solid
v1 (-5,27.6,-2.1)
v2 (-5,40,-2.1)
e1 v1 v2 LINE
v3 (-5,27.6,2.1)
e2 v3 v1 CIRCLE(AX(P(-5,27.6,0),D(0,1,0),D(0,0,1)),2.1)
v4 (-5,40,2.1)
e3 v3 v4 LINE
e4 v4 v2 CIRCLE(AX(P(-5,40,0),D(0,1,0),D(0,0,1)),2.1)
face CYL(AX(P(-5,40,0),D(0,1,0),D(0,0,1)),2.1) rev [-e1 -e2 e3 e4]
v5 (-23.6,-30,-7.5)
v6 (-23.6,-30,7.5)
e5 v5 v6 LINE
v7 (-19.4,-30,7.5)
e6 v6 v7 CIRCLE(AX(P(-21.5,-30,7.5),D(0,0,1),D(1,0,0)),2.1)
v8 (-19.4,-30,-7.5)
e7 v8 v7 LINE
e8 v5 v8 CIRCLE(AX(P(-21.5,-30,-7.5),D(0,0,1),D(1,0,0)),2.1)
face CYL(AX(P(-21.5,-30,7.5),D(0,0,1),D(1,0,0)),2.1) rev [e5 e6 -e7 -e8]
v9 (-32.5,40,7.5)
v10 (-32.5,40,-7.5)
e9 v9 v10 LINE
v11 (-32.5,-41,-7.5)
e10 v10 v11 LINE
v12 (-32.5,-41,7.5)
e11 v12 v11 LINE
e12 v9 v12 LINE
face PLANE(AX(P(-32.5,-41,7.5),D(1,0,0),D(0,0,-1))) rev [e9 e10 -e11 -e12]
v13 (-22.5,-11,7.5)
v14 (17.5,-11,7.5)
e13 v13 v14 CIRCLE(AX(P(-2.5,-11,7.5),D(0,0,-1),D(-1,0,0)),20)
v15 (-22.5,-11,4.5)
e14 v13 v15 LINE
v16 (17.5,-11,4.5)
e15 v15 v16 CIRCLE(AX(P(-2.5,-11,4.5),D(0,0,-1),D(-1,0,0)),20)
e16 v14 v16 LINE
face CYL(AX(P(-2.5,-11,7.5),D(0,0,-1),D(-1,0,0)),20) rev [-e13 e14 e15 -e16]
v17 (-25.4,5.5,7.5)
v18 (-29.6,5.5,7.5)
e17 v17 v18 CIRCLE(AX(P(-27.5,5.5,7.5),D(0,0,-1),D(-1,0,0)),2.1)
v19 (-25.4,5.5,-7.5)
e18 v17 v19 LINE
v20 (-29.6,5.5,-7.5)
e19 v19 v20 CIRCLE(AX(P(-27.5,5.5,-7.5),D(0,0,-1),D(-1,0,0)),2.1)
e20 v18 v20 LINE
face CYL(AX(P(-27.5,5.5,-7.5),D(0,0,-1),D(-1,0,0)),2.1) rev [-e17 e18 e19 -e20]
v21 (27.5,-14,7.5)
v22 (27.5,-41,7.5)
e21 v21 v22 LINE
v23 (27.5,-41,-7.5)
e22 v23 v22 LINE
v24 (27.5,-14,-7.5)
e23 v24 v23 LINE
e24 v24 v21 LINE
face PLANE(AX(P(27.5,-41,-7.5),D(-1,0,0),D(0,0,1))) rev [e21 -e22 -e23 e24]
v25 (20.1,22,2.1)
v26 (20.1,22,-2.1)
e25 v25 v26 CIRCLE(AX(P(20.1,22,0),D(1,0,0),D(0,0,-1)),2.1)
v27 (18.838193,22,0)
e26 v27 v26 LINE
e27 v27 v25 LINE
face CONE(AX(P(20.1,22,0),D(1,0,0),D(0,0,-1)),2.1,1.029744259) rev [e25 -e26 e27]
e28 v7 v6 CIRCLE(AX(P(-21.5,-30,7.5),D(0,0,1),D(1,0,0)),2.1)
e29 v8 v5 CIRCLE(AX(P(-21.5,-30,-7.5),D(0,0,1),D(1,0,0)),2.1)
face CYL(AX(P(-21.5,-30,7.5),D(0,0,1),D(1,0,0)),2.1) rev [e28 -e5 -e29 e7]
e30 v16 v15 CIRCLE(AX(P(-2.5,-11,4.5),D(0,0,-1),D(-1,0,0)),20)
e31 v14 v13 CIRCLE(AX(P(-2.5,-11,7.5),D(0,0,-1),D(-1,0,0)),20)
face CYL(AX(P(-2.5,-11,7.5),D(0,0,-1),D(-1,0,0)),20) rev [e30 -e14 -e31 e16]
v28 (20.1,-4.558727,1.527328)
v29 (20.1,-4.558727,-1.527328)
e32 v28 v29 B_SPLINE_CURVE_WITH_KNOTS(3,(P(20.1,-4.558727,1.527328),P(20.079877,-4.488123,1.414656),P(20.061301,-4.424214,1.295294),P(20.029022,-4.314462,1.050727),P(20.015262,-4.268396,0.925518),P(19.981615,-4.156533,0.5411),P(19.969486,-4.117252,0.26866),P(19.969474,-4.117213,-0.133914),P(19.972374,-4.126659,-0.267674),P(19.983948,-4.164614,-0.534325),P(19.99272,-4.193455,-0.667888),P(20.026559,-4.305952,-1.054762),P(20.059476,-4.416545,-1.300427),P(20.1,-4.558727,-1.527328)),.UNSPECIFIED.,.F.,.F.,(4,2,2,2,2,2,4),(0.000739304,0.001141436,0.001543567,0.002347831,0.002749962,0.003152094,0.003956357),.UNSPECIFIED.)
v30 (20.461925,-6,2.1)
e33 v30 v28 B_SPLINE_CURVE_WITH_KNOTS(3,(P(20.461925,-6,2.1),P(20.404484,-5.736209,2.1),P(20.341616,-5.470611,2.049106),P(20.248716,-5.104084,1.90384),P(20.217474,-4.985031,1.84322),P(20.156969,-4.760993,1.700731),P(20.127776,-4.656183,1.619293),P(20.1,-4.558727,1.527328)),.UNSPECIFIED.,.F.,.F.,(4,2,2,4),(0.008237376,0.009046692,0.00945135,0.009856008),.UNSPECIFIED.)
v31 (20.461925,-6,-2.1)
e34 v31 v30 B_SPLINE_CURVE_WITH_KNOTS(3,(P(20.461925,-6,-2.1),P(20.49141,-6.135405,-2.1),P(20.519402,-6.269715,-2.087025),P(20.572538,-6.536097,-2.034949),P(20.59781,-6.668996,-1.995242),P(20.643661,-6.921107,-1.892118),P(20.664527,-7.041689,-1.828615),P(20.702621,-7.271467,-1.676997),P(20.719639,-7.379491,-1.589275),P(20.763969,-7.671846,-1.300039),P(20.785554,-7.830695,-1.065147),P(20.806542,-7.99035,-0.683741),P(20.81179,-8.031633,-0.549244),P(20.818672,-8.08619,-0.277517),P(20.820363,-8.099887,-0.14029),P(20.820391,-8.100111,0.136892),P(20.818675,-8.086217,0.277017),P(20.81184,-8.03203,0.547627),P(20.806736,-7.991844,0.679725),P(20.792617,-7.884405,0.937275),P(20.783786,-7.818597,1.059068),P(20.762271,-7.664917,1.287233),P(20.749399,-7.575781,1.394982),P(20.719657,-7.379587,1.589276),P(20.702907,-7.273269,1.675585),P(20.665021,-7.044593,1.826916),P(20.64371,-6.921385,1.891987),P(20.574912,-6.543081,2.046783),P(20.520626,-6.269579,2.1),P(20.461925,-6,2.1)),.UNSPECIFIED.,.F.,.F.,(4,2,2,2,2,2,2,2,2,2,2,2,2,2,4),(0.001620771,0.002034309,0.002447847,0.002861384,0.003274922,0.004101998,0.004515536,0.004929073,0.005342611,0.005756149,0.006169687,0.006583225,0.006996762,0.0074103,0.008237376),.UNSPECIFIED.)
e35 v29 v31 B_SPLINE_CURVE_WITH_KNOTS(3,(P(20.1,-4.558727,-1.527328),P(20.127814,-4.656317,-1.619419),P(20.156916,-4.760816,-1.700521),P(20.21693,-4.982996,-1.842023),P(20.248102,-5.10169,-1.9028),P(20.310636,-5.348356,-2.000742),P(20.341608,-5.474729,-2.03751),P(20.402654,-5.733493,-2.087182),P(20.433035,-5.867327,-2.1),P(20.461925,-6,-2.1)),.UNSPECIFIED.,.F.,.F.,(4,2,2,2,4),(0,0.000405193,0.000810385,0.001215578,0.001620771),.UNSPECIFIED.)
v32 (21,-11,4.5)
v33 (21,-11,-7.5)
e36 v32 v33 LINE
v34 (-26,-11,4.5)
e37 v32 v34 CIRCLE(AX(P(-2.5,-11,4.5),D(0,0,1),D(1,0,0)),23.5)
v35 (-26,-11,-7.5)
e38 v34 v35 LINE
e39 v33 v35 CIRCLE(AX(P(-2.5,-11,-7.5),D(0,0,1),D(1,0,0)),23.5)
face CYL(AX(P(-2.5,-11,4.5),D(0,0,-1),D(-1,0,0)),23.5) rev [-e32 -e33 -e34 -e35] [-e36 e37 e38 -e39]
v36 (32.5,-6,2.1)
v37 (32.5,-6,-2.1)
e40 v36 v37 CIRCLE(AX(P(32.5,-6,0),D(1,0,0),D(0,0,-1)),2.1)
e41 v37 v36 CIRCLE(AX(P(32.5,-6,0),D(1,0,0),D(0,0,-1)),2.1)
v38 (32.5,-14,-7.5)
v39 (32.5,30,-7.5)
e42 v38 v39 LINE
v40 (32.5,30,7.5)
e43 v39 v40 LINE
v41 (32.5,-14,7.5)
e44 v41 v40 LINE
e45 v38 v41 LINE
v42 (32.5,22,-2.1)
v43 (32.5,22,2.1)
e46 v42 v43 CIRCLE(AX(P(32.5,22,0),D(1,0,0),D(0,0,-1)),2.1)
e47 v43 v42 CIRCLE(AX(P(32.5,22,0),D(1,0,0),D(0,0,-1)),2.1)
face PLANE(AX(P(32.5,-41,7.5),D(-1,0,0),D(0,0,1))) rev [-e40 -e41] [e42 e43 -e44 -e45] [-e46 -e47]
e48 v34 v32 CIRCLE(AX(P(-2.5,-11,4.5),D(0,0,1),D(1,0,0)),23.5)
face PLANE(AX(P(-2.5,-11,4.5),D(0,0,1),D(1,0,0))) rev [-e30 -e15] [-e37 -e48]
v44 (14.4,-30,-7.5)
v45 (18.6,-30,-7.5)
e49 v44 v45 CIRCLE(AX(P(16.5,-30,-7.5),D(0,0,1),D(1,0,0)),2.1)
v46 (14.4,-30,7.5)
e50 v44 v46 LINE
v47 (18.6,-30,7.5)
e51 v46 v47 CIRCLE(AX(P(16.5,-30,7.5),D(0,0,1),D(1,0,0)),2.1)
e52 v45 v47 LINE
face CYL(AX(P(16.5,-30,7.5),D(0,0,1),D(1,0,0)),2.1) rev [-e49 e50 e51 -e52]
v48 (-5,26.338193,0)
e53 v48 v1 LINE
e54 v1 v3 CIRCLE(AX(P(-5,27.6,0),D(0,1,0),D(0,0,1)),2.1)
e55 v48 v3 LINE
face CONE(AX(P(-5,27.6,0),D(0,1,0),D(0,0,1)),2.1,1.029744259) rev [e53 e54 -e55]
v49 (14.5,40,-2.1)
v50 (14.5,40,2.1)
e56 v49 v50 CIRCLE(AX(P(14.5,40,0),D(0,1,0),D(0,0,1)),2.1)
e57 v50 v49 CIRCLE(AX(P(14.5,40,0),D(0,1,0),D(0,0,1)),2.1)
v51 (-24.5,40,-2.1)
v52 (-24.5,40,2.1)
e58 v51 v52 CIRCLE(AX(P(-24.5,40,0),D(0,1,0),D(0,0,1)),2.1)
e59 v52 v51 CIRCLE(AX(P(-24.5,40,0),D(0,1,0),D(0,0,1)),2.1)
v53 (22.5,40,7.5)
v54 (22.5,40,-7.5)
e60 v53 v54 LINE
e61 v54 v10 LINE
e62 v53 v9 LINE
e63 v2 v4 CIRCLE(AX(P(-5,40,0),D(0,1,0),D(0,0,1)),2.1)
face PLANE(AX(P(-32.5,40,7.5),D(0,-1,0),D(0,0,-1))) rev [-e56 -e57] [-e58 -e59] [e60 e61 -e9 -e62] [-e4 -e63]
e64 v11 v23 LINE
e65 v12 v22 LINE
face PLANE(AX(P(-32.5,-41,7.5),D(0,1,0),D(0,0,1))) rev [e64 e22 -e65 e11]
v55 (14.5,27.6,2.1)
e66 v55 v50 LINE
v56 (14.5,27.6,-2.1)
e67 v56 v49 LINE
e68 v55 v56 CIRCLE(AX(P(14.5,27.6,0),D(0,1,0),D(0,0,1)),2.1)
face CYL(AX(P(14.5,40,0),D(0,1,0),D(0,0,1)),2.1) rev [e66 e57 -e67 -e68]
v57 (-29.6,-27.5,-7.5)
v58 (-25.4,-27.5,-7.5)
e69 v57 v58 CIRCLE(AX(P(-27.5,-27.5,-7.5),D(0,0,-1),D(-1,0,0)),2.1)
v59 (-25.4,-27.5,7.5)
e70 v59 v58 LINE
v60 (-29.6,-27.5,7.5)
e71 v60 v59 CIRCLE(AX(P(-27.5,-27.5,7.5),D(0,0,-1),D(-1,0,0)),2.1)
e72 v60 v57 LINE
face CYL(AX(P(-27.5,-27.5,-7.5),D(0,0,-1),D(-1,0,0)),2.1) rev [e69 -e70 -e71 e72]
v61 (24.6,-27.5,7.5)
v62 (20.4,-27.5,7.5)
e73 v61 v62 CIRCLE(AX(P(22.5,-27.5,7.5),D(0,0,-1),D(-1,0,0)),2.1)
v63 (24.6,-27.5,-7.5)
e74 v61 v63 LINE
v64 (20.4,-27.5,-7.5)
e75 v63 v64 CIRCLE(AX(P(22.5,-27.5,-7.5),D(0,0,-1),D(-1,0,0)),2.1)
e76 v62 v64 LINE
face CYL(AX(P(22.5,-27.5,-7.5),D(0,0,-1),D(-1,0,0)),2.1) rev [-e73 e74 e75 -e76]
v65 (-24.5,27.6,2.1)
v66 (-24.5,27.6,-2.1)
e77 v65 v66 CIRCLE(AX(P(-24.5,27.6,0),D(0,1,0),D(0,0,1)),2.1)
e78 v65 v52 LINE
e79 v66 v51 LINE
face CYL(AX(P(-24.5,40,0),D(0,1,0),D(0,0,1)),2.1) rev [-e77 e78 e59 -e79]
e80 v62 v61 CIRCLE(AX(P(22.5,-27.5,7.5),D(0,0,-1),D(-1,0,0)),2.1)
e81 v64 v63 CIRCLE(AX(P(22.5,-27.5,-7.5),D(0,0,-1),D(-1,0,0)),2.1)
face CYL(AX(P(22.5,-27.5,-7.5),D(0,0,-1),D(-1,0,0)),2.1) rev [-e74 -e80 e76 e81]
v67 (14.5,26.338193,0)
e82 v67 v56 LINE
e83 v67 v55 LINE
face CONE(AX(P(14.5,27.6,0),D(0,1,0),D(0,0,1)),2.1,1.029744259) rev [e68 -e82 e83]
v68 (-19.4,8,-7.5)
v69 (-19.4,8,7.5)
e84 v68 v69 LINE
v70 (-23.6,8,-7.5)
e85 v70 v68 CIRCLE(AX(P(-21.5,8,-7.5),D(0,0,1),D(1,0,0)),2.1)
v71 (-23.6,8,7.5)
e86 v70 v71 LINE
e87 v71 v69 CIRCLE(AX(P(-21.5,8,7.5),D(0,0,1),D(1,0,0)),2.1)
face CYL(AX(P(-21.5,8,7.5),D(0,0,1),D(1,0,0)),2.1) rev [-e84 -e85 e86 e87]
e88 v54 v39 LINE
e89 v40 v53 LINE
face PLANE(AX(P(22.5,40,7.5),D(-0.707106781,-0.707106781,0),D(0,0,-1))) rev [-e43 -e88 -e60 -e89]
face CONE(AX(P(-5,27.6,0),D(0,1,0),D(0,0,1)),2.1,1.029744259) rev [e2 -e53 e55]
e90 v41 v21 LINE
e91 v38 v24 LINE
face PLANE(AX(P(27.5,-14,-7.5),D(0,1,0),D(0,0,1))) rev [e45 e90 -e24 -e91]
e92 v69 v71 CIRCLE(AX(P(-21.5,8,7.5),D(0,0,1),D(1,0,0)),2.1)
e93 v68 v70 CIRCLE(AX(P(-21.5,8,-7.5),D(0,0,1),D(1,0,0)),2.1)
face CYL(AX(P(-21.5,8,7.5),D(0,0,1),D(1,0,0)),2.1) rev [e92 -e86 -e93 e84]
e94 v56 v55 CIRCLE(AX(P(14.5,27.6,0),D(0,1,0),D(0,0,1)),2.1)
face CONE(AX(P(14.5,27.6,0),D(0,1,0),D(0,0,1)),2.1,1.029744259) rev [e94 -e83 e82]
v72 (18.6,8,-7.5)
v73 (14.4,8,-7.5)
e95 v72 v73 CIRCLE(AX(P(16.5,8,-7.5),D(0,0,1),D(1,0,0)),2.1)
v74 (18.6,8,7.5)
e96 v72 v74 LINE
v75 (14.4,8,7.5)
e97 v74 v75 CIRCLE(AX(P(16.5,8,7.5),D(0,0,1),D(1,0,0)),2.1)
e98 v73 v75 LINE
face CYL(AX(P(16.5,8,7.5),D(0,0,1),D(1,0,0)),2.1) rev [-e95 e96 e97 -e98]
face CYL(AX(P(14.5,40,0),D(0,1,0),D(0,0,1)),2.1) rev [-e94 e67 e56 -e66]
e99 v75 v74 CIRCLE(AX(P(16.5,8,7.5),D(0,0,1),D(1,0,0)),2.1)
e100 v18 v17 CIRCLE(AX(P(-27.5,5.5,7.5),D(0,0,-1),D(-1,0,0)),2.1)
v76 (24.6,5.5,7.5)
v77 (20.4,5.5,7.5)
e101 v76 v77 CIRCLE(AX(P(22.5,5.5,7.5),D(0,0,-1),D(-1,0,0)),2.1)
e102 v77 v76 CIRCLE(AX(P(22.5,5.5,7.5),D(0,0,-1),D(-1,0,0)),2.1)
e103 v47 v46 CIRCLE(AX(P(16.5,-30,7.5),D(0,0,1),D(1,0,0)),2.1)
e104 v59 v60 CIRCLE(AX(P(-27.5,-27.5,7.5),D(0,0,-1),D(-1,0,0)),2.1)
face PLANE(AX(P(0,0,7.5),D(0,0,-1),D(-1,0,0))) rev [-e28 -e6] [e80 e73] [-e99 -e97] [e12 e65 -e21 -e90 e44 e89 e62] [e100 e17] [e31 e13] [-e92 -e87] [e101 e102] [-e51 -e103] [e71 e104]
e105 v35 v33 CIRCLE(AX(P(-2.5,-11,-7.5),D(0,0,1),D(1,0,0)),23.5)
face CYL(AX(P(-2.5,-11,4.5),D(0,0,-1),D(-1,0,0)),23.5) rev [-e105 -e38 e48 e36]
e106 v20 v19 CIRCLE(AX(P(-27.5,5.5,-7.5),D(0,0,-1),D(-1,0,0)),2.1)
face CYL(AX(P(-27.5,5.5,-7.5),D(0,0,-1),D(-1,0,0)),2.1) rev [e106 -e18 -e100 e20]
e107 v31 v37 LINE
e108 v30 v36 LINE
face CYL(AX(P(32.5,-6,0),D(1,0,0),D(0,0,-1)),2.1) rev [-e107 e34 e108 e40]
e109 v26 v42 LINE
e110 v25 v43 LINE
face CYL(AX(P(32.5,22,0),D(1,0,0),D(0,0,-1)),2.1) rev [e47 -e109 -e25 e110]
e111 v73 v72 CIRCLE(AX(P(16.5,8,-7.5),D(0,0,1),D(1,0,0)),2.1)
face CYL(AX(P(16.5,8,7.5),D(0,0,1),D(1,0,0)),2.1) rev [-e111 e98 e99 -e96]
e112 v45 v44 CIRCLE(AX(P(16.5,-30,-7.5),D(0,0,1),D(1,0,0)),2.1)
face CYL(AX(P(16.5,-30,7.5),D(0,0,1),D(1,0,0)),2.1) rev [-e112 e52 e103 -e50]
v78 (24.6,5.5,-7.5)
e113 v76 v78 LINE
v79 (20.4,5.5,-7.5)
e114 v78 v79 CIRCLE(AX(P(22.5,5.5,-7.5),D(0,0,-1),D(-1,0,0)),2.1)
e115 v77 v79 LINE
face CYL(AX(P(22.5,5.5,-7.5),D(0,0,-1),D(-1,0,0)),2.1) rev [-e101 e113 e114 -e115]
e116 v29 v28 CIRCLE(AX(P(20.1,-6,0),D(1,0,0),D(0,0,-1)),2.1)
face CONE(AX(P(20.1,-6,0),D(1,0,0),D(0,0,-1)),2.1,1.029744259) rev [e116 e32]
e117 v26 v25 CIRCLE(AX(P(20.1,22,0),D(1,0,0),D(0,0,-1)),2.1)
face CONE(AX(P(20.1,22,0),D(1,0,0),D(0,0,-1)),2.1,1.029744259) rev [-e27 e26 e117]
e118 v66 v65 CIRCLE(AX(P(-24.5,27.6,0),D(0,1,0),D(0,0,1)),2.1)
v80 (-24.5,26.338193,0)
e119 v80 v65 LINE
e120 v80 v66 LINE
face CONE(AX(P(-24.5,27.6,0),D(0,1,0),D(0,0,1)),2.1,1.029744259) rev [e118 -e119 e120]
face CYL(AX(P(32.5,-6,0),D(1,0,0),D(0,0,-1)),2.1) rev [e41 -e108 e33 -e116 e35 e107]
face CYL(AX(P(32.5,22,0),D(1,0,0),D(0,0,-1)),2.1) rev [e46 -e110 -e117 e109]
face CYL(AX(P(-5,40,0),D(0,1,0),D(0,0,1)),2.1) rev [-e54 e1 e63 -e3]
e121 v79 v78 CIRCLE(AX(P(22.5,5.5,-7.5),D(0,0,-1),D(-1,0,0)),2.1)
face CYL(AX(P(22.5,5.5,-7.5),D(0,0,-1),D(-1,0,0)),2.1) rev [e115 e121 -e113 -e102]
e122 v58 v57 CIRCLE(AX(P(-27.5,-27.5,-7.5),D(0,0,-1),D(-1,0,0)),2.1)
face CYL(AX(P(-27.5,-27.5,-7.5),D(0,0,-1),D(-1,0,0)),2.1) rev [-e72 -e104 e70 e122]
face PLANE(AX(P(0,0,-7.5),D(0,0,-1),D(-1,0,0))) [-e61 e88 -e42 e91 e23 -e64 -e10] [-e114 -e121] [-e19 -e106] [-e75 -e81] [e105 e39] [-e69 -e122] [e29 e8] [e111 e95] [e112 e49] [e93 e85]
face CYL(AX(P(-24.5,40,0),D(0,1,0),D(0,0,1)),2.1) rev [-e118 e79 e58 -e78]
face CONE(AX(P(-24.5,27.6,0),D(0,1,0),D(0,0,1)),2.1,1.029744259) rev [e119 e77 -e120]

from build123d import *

# Parameters (mm, degrees)
SKETCH_1_W             = 65
SKETCH_1_H             = 82
EXTRUDE_1_DEPTH        = 7.5
SKETCH_10_R            = 23.5
CUT_EXTRUDE_1_DEPTH    = 12
SKETCH_12_R            = 20
CUT_EXTRUDE_2_DEPTH    = 54.677276384
SKETCH_13_W            = 5
SKETCH_13_H            = 27
CUT_EXTRUDE_3_DEPTH    = 55.426556018
HOLE_WIZARD_M5_1_D     = 4.2
HOLE_WIZARD_M5_2_D     = 4.2
MOVE_FACE_1_BY         = 1
HOLE_WIZARD_M5_4_D     = 4.2
HOLE_WIZARD_M5_4_DEPTH = 12.4
HOLE_WIZARD_M5_4_TIP   = 1.2618073
CHAMFER_2_SIZE         = 10
HOLE_WIZARD_M5_3_D     = 4.2
HOLE_WIZARD_M5_3_DEPTH = 12.4
HOLE_WIZARD_M5_3_TIP   = 1.2618073


with BuildPart() as part:
    # 草图1 → 凸台-拉伸1 (new, symmetric)
    with BuildSketch(Plane.XY):
        Rectangle(SKETCH_1_W, SKETCH_1_H)
    extrude(amount=EXTRUDE_1_DEPTH, both=True)

    # 草图10 → 切除-拉伸1 (cut)
    with BuildSketch(Plane.XY.offset(-7.5)):
        with Locations((-2.5, -11)):
            Circle(SKETCH_10_R)
    extrude(amount=CUT_EXTRUDE_1_DEPTH, mode=Mode.SUBTRACT)

    # 草图12 → 切除-拉伸2 (cut, through all)
    with BuildSketch(Plane(origin=(0, 0, 4.5), x_dir=(-1, 0, 0), z_dir=(0, 0, -1))):
        with Locations((2.5, -11)):
            Circle(SKETCH_12_R)
    extrude(amount=-CUT_EXTRUDE_2_DEPTH, mode=Mode.SUBTRACT)

    # 草图13 → 切除-拉伸3 (cut, through all)
    with BuildSketch(Plane.XY.offset(7.5)):
        with Locations((30, -27.5)):
            Rectangle(SKETCH_13_W, SKETCH_13_H)
    extrude(amount=-CUT_EXTRUDE_3_DEPTH, mode=Mode.SUBTRACT)

    # M5 螺纹孔1 (through all)
    with Locations(Plane(origin=(0, 0, -7.5), x_dir=(-1, 0, 0), z_dir=(0, 0, -1))):
        with Locations((-22.5, 5.5), (-22.5, -27.5), (27.5, -27.5), (27.5, 5.5)):
            Hole(HOLE_WIZARD_M5_1_D / 2)

    # M5 螺纹孔2 (through all)
    with Locations(Plane.XY.offset(7.5)):
        with Locations((-21.5, 8), (-21.5, -30), (16.5, -30), (16.5, 8)):
            Hole(HOLE_WIZARD_M5_2_D / 2)

    # Move Face 1: a face moved inward by 1.0
    extrude(part.faces().sort_by_distance((0, 41, 0))[0], amount=MOVE_FACE_1_BY, dir=(0, -1, 0), mode=Mode.SUBTRACT)

    # M5 螺纹孔4
    with Locations(Plane(origin=(32.5, 0, 0), x_dir=(0, 0, -1), z_dir=(1, 0, 0))):
        with Locations((0, -6), (0, 22)):
            Hole(HOLE_WIZARD_M5_4_D / 2, depth=HOLE_WIZARD_M5_4_DEPTH)
            with Locations((0, 0, -(HOLE_WIZARD_M5_4_DEPTH + HOLE_WIZARD_M5_4_TIP / 2))):  # 118° drill point
                Cone(0, HOLE_WIZARD_M5_4_D / 2, HOLE_WIZARD_M5_4_TIP, mode=Mode.SUBTRACT)

    # 倒角2
    chamfer_2_edges = [part.edges().sort_by_distance(p)[0] for p in [
        (32.5, 40, 0),
    ]]
    chamfer(chamfer_2_edges, length=CHAMFER_2_SIZE)

    # M5 螺纹孔3
    with Locations(Plane(origin=(0, 40, 0), x_dir=(1, 0, 0), z_dir=(0, 1, 0))):
        with Locations((-24.5, 0), (-5, 0), (14.5, 0)):
            Hole(HOLE_WIZARD_M5_3_D / 2, depth=HOLE_WIZARD_M5_3_DEPTH)
            with Locations((0, 0, -(HOLE_WIZARD_M5_3_DEPTH + HOLE_WIZARD_M5_3_TIP / 2))):  # 118° drill point
                Cone(0, HOLE_WIZARD_M5_3_D / 2, HOLE_WIZARD_M5_3_TIP, mode=Mode.SUBTRACT)


solid = part.part
